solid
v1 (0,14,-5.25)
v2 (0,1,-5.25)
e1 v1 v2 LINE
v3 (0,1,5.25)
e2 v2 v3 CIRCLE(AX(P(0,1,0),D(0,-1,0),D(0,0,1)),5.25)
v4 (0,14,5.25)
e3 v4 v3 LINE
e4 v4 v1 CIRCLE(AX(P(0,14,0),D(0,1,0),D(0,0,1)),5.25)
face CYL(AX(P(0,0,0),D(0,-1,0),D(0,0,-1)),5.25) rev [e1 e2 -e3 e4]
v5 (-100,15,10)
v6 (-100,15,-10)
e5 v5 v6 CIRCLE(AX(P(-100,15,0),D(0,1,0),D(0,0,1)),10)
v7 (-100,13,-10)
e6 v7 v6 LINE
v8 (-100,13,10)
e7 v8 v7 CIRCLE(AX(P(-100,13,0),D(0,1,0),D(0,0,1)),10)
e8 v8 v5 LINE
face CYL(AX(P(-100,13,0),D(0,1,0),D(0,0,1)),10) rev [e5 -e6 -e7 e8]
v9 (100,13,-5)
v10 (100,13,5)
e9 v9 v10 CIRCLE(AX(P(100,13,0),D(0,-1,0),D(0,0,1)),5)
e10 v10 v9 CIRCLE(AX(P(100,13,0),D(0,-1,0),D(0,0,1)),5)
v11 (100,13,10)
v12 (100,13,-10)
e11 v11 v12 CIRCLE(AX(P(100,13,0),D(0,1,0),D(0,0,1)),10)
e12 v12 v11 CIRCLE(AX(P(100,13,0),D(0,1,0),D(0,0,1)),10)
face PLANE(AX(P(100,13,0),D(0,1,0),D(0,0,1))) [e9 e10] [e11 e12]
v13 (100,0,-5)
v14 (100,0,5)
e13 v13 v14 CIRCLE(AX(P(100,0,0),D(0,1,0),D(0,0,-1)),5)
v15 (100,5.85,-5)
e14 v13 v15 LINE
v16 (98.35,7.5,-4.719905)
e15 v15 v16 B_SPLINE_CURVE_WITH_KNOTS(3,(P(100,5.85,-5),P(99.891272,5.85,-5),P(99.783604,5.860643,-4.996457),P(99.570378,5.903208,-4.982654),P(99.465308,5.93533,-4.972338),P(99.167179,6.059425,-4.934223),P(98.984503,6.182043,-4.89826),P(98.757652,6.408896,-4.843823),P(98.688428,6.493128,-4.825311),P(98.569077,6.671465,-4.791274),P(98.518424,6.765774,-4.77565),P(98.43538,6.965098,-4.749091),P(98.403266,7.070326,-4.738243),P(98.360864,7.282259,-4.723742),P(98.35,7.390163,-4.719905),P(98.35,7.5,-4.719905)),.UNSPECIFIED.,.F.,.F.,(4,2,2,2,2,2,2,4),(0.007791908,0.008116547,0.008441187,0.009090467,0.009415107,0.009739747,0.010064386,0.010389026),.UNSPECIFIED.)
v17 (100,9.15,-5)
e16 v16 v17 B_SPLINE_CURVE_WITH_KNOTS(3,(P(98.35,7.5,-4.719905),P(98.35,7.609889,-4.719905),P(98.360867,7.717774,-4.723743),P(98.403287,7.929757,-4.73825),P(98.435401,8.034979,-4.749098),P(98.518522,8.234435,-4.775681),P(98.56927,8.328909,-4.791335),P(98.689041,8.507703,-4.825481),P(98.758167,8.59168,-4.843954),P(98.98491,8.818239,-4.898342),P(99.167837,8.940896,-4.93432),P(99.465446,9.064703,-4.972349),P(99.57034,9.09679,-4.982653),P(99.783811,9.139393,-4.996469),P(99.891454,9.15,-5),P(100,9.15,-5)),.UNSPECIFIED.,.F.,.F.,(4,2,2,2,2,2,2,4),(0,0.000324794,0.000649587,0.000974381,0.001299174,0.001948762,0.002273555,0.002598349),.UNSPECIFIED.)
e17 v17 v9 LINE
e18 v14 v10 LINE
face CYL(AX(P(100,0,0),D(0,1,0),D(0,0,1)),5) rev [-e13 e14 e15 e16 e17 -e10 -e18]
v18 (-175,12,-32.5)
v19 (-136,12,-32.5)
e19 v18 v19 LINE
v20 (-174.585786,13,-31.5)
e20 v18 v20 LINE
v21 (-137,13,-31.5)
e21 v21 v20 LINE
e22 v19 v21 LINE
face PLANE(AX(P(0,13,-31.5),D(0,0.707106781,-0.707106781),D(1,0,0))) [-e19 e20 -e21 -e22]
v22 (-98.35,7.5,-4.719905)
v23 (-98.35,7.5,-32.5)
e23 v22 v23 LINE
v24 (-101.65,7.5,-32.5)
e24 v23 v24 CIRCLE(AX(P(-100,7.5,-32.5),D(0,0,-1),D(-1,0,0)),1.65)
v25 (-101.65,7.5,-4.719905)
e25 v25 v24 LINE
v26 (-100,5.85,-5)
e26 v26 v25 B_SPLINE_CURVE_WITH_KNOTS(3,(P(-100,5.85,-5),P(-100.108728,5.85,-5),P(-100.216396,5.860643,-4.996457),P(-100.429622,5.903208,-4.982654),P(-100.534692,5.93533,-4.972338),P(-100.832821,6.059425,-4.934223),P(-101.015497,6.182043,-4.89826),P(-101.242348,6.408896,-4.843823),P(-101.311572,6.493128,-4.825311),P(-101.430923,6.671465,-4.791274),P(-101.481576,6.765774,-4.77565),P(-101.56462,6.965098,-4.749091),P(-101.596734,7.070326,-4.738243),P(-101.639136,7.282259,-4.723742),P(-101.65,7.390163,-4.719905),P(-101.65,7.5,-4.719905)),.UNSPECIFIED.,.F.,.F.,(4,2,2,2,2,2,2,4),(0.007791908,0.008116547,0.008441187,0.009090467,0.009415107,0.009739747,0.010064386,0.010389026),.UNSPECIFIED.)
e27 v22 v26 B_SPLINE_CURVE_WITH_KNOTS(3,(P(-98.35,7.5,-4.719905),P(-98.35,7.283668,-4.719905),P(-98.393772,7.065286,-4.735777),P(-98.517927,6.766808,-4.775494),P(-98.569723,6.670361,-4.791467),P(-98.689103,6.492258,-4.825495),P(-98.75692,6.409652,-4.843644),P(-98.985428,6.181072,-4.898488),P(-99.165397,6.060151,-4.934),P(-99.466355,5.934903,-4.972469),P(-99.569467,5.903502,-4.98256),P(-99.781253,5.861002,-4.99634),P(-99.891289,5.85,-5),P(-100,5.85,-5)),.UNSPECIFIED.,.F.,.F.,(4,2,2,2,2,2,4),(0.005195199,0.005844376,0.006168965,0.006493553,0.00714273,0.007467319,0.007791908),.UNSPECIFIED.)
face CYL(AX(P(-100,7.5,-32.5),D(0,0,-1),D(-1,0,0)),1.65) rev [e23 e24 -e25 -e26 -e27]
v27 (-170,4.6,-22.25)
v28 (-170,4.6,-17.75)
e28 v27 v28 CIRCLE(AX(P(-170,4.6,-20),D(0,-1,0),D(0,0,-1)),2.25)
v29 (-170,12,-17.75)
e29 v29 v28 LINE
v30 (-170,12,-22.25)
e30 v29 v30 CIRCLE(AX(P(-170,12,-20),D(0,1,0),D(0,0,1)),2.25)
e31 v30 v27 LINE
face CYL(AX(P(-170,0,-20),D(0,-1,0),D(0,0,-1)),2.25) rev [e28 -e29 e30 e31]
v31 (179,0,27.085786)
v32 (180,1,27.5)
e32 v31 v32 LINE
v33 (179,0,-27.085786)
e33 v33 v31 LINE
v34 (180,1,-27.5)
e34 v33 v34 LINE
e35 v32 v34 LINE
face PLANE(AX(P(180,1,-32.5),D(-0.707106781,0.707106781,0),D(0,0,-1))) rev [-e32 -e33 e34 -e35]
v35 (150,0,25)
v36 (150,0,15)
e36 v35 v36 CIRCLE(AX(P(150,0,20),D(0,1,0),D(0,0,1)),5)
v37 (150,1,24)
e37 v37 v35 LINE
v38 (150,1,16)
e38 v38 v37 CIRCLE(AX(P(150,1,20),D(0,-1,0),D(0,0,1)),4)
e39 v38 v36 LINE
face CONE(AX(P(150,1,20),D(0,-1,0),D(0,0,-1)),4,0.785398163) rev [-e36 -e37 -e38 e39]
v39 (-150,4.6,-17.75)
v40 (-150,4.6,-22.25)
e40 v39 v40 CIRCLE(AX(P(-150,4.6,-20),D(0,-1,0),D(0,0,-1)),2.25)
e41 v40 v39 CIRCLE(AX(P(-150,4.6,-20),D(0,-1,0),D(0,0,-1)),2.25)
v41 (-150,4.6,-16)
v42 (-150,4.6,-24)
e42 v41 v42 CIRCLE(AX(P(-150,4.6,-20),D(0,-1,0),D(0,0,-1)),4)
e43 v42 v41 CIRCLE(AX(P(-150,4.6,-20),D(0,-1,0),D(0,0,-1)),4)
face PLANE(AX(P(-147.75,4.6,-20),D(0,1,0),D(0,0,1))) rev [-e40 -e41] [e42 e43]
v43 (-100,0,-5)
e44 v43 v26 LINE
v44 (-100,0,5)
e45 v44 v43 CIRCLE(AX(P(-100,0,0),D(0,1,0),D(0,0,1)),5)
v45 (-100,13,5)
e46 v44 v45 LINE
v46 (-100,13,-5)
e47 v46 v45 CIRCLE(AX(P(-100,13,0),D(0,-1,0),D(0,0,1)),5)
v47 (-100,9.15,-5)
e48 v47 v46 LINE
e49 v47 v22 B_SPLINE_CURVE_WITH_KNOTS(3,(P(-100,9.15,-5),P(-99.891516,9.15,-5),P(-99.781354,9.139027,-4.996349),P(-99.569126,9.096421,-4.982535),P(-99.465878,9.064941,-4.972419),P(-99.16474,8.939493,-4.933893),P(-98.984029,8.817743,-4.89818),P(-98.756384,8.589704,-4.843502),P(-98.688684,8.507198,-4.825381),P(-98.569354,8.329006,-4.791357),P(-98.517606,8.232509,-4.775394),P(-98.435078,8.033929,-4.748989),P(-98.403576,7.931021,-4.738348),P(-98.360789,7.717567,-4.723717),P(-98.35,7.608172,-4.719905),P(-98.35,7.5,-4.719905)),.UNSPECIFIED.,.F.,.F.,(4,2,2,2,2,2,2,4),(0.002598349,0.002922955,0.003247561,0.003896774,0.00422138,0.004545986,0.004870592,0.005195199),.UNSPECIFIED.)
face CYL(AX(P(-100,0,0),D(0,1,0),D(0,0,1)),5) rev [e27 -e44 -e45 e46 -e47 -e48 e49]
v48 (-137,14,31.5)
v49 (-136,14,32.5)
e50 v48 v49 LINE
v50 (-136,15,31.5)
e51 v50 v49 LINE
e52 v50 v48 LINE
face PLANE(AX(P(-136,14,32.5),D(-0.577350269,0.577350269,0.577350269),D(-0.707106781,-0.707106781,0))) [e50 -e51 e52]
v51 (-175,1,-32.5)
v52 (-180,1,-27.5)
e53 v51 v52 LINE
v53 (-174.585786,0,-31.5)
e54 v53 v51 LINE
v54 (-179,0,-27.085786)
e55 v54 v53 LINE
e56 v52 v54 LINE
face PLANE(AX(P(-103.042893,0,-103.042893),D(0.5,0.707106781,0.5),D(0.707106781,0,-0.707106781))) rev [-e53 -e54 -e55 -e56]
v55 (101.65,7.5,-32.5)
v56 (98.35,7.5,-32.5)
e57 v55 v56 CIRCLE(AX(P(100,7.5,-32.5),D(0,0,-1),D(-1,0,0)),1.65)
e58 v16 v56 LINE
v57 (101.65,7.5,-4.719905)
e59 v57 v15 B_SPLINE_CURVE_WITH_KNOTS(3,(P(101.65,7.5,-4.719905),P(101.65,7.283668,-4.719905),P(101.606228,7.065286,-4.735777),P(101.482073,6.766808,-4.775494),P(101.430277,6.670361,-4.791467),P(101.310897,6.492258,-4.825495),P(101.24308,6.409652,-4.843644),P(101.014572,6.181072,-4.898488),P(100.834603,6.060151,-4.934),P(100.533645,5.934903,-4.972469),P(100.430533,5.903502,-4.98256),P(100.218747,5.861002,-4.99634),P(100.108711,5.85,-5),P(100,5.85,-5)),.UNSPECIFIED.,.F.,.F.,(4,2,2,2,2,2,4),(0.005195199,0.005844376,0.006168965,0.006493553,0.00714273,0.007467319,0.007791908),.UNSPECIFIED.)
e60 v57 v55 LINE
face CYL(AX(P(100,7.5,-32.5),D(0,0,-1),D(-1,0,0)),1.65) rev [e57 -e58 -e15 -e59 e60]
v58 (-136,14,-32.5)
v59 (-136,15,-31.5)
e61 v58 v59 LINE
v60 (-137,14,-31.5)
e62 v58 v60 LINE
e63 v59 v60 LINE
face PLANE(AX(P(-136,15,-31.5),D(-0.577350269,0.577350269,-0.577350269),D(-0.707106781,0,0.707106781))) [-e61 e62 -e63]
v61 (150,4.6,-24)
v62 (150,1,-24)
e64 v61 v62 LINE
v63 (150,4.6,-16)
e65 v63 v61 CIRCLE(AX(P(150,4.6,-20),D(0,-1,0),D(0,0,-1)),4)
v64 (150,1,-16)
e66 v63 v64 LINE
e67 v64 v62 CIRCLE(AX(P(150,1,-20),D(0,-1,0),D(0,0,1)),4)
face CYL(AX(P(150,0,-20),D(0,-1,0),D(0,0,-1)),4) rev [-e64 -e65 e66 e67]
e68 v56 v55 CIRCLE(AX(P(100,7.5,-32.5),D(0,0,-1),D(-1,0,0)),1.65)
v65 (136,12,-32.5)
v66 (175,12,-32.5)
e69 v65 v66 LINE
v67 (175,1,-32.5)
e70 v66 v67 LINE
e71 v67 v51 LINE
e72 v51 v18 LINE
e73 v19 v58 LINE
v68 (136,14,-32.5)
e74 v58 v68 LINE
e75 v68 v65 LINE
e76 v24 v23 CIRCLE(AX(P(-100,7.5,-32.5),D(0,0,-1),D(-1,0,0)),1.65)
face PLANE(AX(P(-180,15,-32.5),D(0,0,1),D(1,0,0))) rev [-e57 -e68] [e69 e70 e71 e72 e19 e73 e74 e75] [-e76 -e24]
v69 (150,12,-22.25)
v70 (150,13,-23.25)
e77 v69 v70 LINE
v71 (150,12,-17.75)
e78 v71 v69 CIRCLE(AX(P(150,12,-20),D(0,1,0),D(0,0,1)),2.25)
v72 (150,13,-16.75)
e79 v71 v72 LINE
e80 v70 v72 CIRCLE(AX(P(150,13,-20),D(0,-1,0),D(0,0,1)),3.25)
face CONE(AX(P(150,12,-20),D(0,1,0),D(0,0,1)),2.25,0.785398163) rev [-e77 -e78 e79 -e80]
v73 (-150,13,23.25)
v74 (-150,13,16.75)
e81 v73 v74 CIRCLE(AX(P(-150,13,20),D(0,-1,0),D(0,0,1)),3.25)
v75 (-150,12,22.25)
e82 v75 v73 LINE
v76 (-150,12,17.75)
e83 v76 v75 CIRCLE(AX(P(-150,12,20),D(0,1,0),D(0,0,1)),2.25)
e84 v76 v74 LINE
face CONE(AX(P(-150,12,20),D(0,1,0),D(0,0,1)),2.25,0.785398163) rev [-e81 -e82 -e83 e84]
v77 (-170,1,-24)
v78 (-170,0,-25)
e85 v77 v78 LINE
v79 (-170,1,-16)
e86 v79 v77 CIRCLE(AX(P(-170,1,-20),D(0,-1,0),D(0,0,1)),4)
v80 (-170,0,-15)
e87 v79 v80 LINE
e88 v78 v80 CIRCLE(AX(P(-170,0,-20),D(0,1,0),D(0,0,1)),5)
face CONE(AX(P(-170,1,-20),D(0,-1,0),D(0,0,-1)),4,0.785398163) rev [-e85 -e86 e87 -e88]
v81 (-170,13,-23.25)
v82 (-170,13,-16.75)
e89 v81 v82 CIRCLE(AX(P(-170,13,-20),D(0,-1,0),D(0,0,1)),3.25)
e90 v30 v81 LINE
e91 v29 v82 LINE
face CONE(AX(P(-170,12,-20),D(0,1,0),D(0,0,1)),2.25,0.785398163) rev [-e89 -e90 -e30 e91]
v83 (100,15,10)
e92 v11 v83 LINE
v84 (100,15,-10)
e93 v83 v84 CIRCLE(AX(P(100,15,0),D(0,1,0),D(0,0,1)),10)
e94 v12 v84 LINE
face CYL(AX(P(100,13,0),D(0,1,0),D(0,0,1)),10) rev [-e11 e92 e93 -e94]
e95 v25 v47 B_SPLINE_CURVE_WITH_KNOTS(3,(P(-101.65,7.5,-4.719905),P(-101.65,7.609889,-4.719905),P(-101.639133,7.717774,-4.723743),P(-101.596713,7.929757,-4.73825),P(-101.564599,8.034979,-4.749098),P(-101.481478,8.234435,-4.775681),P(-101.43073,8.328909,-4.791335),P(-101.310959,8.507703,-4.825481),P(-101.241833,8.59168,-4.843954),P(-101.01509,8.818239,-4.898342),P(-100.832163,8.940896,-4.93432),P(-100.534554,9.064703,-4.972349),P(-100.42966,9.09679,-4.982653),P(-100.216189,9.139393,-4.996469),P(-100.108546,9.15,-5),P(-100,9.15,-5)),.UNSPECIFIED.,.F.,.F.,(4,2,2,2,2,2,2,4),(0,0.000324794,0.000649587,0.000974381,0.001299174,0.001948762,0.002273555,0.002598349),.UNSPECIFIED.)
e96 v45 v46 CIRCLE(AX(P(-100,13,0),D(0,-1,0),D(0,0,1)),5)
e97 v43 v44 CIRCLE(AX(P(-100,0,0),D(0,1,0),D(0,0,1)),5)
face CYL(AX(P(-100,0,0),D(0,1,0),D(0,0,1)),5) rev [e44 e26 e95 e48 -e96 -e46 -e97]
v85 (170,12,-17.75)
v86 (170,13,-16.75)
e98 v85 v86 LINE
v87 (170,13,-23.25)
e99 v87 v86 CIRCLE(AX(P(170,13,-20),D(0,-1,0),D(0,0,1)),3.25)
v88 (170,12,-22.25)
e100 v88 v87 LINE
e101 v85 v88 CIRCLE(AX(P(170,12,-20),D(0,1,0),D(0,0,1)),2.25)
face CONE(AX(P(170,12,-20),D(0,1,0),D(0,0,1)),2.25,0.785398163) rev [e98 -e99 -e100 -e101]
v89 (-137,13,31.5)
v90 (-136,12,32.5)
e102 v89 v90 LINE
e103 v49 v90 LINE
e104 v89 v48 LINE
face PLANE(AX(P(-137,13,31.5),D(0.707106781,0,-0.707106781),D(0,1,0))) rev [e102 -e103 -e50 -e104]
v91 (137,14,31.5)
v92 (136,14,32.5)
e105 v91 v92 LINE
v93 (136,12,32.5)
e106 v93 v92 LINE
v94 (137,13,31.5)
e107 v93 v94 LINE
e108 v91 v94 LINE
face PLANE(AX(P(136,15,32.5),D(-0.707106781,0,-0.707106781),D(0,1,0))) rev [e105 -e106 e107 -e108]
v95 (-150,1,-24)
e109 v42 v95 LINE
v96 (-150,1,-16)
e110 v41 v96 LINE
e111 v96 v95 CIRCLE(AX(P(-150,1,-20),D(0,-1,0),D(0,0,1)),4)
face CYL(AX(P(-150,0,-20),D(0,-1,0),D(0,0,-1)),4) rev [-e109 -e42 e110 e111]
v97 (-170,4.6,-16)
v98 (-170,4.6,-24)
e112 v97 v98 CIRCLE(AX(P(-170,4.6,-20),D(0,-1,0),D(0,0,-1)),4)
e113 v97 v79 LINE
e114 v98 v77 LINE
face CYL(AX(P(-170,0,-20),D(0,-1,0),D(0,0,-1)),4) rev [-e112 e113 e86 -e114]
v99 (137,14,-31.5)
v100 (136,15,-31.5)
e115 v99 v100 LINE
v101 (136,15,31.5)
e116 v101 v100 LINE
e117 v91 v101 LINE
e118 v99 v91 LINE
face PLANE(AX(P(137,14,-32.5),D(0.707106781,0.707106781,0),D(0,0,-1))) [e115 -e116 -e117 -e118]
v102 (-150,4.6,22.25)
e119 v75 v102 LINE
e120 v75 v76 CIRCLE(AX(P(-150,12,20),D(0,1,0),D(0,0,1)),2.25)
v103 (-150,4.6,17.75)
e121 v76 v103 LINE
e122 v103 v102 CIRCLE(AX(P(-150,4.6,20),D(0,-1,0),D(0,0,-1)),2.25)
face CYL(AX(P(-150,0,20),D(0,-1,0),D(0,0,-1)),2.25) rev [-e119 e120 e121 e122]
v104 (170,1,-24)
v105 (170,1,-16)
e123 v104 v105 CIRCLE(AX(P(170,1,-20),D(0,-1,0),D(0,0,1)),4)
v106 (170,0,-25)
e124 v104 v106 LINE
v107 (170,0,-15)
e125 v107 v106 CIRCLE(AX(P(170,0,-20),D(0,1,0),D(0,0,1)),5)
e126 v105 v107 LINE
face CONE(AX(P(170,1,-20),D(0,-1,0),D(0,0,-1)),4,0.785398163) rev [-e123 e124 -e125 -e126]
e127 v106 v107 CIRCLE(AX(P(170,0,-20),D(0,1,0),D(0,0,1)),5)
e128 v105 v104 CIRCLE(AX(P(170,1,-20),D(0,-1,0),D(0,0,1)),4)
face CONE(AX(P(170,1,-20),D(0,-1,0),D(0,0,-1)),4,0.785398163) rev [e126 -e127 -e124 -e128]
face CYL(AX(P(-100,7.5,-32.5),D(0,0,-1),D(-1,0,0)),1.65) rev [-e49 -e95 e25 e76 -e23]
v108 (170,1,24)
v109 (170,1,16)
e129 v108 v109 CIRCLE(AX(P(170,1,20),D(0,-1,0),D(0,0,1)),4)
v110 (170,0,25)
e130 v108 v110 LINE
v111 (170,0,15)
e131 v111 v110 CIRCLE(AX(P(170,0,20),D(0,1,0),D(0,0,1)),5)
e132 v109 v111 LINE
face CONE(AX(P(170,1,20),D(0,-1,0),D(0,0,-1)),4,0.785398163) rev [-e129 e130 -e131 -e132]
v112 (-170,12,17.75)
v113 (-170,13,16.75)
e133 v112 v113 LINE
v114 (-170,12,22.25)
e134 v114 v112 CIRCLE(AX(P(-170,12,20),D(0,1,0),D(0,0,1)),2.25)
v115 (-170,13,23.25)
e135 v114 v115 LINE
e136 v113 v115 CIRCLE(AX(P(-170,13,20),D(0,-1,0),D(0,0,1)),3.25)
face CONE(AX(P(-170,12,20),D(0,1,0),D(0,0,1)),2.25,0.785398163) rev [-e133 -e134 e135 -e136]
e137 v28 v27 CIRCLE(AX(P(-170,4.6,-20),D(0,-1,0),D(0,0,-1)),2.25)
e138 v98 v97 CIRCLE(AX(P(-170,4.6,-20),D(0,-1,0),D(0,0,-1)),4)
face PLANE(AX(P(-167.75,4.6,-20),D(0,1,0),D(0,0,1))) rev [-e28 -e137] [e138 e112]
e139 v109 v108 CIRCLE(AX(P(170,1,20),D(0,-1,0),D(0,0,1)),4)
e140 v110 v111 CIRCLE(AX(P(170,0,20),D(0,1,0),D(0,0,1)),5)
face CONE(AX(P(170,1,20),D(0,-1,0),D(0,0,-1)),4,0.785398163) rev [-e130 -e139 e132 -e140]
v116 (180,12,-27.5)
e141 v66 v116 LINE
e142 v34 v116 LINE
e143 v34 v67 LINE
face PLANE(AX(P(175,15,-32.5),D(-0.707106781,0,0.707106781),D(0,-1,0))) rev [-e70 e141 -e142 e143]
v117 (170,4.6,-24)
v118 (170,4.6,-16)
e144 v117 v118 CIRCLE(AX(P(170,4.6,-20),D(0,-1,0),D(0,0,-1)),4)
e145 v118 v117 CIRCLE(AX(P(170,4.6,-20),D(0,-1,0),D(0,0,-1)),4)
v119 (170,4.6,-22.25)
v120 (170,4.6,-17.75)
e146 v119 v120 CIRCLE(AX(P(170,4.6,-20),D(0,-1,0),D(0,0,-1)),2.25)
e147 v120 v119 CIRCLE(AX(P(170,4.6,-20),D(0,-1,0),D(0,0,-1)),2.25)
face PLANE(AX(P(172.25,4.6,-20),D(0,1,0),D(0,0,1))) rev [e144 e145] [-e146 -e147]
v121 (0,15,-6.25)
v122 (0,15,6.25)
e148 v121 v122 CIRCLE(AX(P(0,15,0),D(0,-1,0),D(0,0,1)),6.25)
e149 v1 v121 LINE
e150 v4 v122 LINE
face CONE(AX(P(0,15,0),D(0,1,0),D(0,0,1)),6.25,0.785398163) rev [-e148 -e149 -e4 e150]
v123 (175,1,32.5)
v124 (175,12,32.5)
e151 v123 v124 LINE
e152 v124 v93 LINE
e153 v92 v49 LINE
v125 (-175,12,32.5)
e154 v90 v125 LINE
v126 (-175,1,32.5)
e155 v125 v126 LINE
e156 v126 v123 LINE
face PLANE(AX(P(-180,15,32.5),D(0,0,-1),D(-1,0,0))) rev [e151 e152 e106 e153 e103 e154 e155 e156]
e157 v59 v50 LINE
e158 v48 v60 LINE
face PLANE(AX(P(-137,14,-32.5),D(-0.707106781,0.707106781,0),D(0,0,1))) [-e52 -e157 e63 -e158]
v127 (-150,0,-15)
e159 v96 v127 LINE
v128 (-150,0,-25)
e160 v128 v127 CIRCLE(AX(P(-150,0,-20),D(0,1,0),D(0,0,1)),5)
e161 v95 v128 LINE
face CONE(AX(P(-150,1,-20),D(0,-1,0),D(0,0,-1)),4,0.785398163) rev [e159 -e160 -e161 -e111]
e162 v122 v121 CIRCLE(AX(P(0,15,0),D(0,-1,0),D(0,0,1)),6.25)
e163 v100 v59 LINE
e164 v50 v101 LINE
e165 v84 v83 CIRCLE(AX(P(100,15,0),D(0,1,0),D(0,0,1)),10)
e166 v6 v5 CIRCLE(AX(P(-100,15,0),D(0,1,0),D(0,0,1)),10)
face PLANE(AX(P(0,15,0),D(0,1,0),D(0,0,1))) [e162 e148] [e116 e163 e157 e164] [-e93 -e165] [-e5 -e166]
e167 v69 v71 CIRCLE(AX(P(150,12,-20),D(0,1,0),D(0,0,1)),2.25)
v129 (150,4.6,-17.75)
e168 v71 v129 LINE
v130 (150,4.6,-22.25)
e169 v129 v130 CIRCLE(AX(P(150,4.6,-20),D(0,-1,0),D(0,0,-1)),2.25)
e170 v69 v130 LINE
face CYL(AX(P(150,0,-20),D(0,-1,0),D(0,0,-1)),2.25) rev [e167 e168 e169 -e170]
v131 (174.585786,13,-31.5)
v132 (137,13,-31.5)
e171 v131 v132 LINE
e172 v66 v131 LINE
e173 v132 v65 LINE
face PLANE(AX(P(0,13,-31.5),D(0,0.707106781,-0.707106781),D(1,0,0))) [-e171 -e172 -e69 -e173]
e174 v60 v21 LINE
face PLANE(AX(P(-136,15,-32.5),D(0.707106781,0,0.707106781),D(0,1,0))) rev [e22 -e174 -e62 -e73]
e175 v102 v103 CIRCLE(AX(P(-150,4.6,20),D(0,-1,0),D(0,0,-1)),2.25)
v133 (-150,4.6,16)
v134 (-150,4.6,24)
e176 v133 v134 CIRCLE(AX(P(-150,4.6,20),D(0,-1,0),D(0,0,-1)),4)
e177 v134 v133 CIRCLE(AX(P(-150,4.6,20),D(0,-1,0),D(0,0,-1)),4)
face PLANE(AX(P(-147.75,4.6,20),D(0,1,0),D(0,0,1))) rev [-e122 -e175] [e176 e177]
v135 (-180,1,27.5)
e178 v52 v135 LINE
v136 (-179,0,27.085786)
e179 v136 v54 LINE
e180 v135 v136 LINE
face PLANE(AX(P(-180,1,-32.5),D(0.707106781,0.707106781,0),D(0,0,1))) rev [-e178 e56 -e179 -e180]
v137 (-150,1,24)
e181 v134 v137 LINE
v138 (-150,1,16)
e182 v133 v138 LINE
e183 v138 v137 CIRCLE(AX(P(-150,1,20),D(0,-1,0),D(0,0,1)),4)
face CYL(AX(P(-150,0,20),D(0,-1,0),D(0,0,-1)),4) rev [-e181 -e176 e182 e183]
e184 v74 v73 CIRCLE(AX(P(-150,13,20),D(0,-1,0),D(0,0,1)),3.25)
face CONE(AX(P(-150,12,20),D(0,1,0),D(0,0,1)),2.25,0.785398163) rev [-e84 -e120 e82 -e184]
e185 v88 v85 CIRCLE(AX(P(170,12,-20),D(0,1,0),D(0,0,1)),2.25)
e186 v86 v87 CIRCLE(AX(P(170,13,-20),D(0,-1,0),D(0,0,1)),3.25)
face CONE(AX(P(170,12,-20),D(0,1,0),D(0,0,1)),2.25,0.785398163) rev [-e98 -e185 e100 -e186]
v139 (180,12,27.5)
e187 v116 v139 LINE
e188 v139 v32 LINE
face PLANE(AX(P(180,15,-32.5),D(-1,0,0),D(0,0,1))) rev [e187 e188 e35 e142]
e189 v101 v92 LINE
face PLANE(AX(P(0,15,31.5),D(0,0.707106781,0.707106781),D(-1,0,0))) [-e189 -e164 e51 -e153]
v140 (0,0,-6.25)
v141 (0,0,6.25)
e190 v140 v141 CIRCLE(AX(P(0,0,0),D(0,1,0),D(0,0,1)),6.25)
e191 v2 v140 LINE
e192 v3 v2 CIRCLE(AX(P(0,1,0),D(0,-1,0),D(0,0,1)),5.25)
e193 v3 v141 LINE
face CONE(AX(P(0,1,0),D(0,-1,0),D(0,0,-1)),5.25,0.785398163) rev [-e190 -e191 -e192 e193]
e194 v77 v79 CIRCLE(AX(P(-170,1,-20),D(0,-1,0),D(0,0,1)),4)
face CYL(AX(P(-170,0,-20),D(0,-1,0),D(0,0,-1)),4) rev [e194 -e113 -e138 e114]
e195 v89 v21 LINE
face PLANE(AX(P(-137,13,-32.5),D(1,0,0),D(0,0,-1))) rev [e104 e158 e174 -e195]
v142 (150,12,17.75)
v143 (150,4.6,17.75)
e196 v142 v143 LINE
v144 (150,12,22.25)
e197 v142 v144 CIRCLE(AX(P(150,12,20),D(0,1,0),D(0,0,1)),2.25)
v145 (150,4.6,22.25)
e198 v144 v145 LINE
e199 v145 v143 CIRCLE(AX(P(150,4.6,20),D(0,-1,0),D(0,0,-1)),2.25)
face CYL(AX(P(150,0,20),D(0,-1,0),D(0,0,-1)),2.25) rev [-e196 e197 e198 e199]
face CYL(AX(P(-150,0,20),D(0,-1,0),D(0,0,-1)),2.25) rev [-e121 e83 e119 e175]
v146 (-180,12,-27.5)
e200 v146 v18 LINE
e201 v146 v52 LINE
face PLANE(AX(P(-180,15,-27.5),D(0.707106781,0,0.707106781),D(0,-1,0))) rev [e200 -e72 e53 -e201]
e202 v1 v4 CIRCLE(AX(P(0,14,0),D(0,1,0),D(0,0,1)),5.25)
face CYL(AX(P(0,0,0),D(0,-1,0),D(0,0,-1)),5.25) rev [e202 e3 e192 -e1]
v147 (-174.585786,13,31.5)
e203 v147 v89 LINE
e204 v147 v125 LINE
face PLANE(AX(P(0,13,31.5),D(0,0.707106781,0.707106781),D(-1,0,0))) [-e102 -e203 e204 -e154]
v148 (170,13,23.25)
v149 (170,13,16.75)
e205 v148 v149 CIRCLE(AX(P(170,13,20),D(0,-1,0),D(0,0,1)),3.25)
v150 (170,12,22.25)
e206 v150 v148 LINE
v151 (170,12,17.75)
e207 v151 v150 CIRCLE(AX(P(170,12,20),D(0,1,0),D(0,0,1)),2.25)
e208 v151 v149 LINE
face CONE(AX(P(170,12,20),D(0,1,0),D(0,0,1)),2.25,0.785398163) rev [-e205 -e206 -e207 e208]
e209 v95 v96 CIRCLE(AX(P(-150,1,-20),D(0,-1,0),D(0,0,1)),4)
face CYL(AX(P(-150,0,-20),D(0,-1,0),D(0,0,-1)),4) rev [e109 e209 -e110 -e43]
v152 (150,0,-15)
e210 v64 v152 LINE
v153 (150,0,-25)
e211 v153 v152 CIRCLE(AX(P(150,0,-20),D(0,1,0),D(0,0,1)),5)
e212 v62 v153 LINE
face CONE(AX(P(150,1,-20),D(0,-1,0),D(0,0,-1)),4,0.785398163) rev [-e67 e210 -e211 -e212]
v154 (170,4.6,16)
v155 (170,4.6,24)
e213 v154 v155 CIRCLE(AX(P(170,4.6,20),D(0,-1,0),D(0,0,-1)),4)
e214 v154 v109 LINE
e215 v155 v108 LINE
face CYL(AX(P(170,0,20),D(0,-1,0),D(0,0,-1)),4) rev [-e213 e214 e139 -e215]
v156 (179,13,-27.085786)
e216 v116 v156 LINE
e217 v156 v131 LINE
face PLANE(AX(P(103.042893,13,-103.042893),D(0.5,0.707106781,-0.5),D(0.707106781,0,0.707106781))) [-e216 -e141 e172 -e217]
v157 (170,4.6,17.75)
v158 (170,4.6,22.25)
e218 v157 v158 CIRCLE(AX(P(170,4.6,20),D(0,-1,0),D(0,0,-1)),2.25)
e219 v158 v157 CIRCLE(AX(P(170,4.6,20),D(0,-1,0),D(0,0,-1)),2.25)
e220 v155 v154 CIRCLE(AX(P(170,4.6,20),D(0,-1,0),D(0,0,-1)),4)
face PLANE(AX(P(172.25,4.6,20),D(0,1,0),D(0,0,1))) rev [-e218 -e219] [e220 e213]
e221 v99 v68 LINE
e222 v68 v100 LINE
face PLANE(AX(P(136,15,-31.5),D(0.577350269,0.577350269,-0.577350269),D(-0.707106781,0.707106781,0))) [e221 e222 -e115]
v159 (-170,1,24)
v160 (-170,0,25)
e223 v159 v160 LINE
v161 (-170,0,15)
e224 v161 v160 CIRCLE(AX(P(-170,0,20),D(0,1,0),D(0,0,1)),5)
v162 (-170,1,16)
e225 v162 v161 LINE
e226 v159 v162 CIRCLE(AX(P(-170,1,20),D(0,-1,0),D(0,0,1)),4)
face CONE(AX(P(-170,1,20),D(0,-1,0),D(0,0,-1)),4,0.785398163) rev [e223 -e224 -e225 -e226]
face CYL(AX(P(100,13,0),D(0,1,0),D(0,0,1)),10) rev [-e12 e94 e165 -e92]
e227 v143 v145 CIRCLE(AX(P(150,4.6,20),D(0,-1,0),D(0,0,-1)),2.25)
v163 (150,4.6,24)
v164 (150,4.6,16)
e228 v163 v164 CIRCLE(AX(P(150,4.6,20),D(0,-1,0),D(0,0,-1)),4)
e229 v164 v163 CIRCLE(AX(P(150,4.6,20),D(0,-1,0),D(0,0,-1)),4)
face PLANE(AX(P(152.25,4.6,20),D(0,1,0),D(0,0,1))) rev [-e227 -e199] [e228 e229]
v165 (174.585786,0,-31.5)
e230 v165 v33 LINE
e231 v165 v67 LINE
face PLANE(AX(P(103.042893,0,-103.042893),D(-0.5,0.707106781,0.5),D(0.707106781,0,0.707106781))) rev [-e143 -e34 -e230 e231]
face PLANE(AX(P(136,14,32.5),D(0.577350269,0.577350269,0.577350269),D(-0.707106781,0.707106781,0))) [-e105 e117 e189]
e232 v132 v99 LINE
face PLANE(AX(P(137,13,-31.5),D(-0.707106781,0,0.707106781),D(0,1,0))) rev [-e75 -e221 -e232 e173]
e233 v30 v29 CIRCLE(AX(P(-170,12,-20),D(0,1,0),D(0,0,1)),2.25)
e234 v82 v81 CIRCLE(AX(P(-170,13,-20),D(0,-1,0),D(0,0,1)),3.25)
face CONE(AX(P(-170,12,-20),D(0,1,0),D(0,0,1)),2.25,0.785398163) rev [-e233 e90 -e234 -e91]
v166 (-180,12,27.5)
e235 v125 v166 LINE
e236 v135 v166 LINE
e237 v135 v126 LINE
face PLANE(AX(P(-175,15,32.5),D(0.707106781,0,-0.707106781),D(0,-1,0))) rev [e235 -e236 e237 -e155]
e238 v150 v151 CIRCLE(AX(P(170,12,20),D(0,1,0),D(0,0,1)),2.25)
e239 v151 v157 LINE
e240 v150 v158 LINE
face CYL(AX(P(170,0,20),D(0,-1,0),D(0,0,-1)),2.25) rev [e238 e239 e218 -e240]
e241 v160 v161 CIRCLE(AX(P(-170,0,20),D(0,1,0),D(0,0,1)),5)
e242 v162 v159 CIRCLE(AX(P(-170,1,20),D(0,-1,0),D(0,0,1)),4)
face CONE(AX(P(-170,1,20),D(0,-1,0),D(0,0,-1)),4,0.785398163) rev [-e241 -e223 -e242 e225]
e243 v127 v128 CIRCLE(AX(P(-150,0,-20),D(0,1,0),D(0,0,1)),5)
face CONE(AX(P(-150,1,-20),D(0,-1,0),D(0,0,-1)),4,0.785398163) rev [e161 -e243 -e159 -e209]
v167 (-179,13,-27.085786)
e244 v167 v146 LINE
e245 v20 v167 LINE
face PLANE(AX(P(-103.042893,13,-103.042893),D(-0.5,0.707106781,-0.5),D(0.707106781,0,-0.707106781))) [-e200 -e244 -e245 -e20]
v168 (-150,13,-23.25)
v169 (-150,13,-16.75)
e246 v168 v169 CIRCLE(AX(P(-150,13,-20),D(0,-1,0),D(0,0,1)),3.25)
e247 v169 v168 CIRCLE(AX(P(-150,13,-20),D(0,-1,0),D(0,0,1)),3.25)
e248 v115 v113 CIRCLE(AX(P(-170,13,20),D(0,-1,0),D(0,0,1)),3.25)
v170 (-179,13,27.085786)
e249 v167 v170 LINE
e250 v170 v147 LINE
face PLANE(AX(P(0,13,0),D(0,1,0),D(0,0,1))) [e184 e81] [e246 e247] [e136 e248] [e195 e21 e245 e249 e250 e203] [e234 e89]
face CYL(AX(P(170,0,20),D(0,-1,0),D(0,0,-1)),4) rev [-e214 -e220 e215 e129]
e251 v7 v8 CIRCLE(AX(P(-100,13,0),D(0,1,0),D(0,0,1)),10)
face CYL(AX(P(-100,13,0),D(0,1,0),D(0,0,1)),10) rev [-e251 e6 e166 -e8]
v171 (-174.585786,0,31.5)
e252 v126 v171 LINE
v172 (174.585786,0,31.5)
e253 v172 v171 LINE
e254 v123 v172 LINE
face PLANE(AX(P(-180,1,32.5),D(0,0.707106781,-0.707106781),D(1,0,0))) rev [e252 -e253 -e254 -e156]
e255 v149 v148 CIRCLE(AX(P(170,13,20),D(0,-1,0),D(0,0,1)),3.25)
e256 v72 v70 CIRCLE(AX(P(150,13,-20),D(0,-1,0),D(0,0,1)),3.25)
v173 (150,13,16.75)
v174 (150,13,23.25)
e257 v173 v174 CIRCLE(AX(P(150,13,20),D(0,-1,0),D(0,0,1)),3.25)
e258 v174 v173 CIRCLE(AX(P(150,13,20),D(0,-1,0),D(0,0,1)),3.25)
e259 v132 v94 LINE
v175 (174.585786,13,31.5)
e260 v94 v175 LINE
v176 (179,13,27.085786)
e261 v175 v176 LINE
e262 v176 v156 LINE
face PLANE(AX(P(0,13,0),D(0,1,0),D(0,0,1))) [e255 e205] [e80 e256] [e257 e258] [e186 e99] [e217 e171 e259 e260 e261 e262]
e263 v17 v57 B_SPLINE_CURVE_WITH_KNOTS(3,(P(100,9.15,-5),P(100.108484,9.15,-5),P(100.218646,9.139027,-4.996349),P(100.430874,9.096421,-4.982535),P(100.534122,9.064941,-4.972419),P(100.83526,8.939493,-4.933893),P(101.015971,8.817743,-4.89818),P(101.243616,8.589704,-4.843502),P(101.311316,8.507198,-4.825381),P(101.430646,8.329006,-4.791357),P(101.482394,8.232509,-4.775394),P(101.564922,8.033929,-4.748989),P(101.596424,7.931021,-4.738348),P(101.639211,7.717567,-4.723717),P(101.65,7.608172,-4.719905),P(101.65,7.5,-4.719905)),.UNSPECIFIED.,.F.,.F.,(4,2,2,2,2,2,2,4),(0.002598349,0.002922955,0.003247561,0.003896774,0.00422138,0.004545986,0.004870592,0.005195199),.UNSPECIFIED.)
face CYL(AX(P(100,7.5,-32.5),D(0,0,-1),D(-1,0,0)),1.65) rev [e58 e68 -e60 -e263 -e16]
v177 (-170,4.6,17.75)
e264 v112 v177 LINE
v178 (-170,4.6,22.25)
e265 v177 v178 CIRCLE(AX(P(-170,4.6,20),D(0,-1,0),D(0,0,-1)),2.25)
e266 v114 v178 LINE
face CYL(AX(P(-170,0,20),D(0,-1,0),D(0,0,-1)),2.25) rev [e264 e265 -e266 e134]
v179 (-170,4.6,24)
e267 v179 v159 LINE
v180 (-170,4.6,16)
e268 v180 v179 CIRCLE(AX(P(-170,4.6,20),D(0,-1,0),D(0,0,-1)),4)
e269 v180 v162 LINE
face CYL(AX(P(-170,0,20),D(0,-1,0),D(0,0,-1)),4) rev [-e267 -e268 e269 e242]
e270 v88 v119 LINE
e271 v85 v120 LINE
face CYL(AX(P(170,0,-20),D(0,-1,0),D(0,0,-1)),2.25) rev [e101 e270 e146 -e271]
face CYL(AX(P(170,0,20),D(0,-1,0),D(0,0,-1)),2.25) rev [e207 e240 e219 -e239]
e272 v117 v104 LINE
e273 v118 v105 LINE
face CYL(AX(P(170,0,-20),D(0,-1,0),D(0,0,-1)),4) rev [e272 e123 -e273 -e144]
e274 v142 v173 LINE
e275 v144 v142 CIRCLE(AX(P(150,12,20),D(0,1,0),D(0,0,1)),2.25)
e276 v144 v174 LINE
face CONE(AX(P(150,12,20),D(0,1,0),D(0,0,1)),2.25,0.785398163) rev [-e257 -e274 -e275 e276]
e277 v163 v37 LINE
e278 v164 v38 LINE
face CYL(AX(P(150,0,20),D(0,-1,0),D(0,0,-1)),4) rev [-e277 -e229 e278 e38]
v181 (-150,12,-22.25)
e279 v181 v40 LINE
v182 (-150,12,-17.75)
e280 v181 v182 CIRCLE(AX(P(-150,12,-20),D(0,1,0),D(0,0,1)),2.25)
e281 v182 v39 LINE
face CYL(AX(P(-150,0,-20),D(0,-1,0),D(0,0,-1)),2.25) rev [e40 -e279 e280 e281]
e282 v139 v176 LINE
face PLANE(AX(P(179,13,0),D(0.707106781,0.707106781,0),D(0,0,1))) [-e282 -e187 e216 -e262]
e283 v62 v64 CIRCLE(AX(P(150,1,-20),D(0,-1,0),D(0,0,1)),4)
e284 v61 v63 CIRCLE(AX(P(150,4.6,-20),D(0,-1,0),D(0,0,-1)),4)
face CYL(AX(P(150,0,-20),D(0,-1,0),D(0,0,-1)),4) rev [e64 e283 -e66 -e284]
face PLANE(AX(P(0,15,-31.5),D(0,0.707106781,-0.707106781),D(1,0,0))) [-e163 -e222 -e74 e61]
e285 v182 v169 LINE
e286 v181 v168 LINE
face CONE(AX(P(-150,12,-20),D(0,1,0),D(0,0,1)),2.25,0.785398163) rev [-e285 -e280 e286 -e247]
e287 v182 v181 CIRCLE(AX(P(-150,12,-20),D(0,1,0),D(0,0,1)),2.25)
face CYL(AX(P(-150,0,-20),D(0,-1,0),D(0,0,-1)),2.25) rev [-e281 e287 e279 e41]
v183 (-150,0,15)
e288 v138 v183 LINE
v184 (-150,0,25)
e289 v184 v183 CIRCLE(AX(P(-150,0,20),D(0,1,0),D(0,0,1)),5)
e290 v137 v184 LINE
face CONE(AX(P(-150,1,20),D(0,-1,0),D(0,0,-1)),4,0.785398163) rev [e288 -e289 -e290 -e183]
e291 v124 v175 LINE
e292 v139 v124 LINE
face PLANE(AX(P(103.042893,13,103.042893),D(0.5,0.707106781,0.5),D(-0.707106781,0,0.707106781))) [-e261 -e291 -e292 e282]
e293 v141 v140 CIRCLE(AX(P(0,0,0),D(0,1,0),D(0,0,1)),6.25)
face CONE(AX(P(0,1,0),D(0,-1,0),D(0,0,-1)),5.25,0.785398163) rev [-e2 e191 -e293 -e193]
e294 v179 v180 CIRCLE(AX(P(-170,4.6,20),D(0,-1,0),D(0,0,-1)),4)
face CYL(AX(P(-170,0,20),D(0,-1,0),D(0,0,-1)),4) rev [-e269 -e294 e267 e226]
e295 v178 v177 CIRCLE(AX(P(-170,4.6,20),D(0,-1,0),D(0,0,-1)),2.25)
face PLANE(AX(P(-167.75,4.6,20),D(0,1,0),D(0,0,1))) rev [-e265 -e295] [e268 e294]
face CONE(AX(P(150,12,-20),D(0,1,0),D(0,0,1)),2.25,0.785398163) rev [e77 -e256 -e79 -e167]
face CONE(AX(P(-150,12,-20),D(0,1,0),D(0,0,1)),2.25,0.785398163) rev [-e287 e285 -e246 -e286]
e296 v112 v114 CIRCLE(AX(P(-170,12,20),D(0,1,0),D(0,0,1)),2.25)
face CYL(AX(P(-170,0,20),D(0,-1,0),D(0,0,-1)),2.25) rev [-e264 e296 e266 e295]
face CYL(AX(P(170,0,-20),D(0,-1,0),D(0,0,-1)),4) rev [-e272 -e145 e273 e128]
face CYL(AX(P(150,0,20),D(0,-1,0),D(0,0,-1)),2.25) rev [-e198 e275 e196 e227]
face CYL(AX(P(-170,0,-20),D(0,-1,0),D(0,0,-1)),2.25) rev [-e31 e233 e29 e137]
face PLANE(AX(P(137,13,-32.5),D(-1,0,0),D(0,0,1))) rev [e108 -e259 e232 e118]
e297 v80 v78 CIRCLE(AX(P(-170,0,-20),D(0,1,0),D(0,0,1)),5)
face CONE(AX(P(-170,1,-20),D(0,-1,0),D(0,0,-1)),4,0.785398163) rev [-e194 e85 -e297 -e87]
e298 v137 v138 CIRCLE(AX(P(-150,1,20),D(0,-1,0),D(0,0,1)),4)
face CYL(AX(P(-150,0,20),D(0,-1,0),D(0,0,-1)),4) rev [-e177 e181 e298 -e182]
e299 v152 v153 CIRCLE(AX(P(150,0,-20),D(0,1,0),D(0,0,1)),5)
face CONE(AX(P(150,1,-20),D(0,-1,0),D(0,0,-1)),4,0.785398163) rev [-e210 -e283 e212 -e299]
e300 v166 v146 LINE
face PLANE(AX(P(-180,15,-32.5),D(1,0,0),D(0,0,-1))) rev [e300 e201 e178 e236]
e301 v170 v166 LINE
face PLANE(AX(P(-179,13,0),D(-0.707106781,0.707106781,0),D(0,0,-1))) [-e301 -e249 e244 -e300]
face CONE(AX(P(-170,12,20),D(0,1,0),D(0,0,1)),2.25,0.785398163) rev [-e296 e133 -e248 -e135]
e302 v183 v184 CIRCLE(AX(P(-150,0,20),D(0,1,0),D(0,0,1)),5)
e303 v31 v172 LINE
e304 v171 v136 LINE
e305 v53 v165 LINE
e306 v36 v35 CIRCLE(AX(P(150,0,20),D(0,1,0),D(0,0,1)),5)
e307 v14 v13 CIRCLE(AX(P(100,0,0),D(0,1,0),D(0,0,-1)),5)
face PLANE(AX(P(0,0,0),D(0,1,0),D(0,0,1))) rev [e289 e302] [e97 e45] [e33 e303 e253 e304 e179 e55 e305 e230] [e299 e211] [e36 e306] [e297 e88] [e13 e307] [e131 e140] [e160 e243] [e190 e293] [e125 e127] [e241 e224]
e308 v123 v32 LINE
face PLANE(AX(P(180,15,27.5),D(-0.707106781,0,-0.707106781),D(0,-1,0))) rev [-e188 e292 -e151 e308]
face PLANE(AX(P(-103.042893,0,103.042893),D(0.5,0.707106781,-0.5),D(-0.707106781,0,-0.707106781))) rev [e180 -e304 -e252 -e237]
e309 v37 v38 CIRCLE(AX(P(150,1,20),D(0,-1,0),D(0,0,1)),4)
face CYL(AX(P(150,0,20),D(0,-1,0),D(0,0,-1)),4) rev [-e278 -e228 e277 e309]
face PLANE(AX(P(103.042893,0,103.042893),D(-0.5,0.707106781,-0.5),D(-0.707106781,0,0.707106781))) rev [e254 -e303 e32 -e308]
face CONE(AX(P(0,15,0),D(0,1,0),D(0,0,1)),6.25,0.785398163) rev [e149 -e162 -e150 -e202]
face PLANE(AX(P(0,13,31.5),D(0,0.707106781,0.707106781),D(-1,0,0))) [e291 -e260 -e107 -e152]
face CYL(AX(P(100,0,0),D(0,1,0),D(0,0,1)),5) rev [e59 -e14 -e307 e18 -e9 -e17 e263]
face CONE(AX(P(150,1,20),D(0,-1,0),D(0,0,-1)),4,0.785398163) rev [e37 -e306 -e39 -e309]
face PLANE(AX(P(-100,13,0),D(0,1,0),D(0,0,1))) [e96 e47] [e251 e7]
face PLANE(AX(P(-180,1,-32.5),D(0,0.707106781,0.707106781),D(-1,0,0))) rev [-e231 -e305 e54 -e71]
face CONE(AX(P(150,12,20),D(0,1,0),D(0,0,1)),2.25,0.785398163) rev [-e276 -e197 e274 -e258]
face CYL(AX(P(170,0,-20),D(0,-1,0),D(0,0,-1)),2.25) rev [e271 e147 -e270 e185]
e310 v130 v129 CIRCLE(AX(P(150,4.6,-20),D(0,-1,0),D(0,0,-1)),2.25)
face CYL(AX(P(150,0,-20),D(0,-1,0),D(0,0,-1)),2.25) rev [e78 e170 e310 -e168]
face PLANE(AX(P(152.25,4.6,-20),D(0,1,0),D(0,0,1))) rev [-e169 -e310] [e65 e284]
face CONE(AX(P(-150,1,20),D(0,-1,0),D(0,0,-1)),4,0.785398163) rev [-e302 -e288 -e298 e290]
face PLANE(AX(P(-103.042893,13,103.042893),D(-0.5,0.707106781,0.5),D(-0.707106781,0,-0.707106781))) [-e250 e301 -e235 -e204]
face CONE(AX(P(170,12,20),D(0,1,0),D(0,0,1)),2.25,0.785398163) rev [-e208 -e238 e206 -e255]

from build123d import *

# Parameters (mm, degrees)
SKETCH1_W                                          = 360
SKETCH1_H                                          = 65
BOSS_EXTRUDE1_DEPTH                                = 15
SKETCH2_W                                          = 43
SKETCH2_H                                          = 65
CUT_EXTRUDE1_DEPTH                                 = 2
HOLE_SIZE_BASED_ON_SOCKET_HEAD_CAP_SCR_D           = 4.5
HOLE_SIZE_BASED_ON_SOCKET_HEAD_CAP_SCR_CBORE_D     = 8
HOLE_SIZE_BASED_ON_SOCKET_HEAD_CAP_SCR_CBORE_DEPTH = 4.6
M12X1_5_TAPPED_HOLE1_D                             = 10.5
CHAMFER1_SIZE                                      = 5
CHAMFER2_SIZE                                      = 1
SKETCH7_R                                          = 5
CUT_EXTRUDE2_DEPTH                                 = 184.524521522
M4_TAPPED_HOLE1_REACH                              = 193.964
M4_TAPPED_HOLE1_BORE_R                             = 1.65
SKETCH10_R                                         = 10
CUT_EXTRUDE3_DEPTH                                 = 2


with BuildPart() as part:
    # Sketch1 → Boss-Extrude1 (new body)
    with BuildSketch(Plane(origin=(0, 0, 0), x_dir=(1, 0, 0), z_dir=(0, 1, 0))):
        Rectangle(SKETCH1_W, SKETCH1_H)
    extrude(amount=BOSS_EXTRUDE1_DEPTH)

    # Sketch2 → Cut-Extrude1 (cut)
    with BuildSketch(Plane(origin=(0, 15, 0), x_dir=(1, 0, 0), z_dir=(0, 1, 0))):
        with Locations((-158.5, 0)):
            Rectangle(SKETCH2_W, SKETCH2_H)
        with Locations((158.5, 0)):
            Rectangle(SKETCH2_W, SKETCH2_H)
    extrude(amount=-CUT_EXTRUDE1_DEPTH, mode=Mode.SUBTRACT)

    # Hole size (%based on) socket head cap screw type 1 (through all)
    with Locations(Plane(origin=(0, 0, 0), x_dir=(-1, 0, 0), z_dir=(0, -1, 0))):
        with Locations((170, -20), (150, -20), (170, 20), (150, 20), (-150, 20), (-170, 20), (-150, -20), (-170, -20)):
            CounterBoreHole(HOLE_SIZE_BASED_ON_SOCKET_HEAD_CAP_SCR_D / 2, HOLE_SIZE_BASED_ON_SOCKET_HEAD_CAP_SCR_CBORE_D / 2, HOLE_SIZE_BASED_ON_SOCKET_HEAD_CAP_SCR_CBORE_DEPTH)

    # M12x1.5 Tapped Hole1 (through all)
    with Locations(Plane(origin=(0, 0, 0), x_dir=(-1, 0, 0), z_dir=(0, -1, 0))):
        with Locations((0, 0)):
            Hole(M12X1_5_TAPPED_HOLE1_D / 2)

    # Chamfer1
    chamfer1_edges = [part.edges().sort_by_distance(p)[0] for p in [
        (180, 6.5, 32.5),
        (-180, 6.5, 32.5),
        (-180, 6.5, -32.5),
        (180, 6.5, -32.5),
    ]]
    chamfer(chamfer1_edges, length=CHAMFER1_SIZE)

    # Chamfer2
    chamfer2_edges = [part.edges().sort_by_distance(p)[0] for p in [
        (-5.25, 0, 0),
        (-5.25, 15, 0),
        (-156, 13, 32.5),
        (0, 0, 32.5),
        (180, 0, 0),
        (-180, 0, 0),
        (0, 0, -32.5),
        (177.5, 0, -30),
        (177.5, 0, 30),
        (-177.5, 0, -30),
        (-177.5, 0, 30),
        (-180, 13, 0),
        (-177.5, 13, -30),
        (0, 15, -32.5),
        (-177.5, 13, 30),
        (156, 13, -32.5),
        (180, 13, 0),
        (177.5, 13, -30),
        (177.5, 13, 30),
        (0, 15, 32.5),
        (-156, 13, -32.5),
        (-137, 14, -32.5),
        (-137, 14, 32.5),
        (-137, 15, 0),
        (137, 14, -32.5),
        (156, 13, 32.5),
        (137, 14, 32.5),
        (137, 15, 0),
        (167.75, 13, 20),
        (174, 0, 20),
        (147.75, 13, 20),
        (154, 0, 20),
        (167.75, 13, -20),
        (174, 0, -20),
        (147.75, 13, -20),
        (154, 0, -20),
        (-152.25, 13, -20),
        (-146, 0, -20),
        (-172.25, 13, -20),
        (-166, 0, -20),
        (-152.25, 13, 20),
        (-146, 0, 20),
        (-172.25, 13, 20),
        (-166, 0, 20),
    ]]
    chamfer(chamfer2_edges, length=CHAMFER2_SIZE)

    # Sketch7 → Cut-Extrude2 (cut, through all)
    with BuildSketch(Plane(origin=(0, 15, 0), x_dir=(1, 0, 0), z_dir=(0, 1, 0))):
        with Locations(Location((-100, 0, 0), (0, 0, 270))):
            Circle(SKETCH7_R)
        with Locations(Location((100, 0, 0), (0, 0, 90))):
            Circle(SKETCH7_R)
    extrude(amount=-CUT_EXTRUDE2_DEPTH, mode=Mode.SUBTRACT)

    # M4 Tapped Hole1 bore → M4 Tapped Hole1 (cut, up to next)
    with BuildSketch(Plane(origin=(0, 0, -32.5), x_dir=(-1, 0, 0), z_dir=(0, 0, -1)), mode=Mode.PRIVATE) as m4_tapped_hole1_sk1:
        with Locations((-100, 7.5)):
            Circle(M4_TAPPED_HOLE1_BORE_R)
    m4_tapped_hole1_tool1 = extrude(m4_tapped_hole1_sk1.sketch, amount=-M4_TAPPED_HOLE1_REACH, mode=Mode.PRIVATE) & part.part
    # M4 Tapped Hole1 bore → M4 Tapped Hole1 (cut, up to next)
    with BuildSketch(Plane(origin=(0, 0, -32.5), x_dir=(-1, 0, 0), z_dir=(0, 0, -1)), mode=Mode.PRIVATE) as m4_tapped_hole1_sk2:
        with Locations((100, 7.5)):
            Circle(M4_TAPPED_HOLE1_BORE_R)
    m4_tapped_hole1_tool2 = extrude(m4_tapped_hole1_sk2.sketch, amount=-M4_TAPPED_HOLE1_REACH, mode=Mode.PRIVATE) & part.part
    add(m4_tapped_hole1_tool1.solids().sort_by_distance((100, 7.5, -32.5))[0], mode=Mode.SUBTRACT)
    add(m4_tapped_hole1_tool2.solids().sort_by_distance((-100, 7.5, -32.5))[0], mode=Mode.SUBTRACT)

    # Sketch10 → Cut-Extrude3 (cut)
    with BuildSketch(Plane(origin=(0, 15, 0), x_dir=(1, 0, 0), z_dir=(0, 1, 0))):
        with Locations(Location((-100, 0, 0), (0, 0, 270))):
            Circle(SKETCH10_R)
        with Locations(Location((100, 0, 0), (0, 0, 270))):
            Circle(SKETCH10_R)
    extrude(amount=-CUT_EXTRUDE3_DEPTH, mode=Mode.SUBTRACT)


solid = part.part
